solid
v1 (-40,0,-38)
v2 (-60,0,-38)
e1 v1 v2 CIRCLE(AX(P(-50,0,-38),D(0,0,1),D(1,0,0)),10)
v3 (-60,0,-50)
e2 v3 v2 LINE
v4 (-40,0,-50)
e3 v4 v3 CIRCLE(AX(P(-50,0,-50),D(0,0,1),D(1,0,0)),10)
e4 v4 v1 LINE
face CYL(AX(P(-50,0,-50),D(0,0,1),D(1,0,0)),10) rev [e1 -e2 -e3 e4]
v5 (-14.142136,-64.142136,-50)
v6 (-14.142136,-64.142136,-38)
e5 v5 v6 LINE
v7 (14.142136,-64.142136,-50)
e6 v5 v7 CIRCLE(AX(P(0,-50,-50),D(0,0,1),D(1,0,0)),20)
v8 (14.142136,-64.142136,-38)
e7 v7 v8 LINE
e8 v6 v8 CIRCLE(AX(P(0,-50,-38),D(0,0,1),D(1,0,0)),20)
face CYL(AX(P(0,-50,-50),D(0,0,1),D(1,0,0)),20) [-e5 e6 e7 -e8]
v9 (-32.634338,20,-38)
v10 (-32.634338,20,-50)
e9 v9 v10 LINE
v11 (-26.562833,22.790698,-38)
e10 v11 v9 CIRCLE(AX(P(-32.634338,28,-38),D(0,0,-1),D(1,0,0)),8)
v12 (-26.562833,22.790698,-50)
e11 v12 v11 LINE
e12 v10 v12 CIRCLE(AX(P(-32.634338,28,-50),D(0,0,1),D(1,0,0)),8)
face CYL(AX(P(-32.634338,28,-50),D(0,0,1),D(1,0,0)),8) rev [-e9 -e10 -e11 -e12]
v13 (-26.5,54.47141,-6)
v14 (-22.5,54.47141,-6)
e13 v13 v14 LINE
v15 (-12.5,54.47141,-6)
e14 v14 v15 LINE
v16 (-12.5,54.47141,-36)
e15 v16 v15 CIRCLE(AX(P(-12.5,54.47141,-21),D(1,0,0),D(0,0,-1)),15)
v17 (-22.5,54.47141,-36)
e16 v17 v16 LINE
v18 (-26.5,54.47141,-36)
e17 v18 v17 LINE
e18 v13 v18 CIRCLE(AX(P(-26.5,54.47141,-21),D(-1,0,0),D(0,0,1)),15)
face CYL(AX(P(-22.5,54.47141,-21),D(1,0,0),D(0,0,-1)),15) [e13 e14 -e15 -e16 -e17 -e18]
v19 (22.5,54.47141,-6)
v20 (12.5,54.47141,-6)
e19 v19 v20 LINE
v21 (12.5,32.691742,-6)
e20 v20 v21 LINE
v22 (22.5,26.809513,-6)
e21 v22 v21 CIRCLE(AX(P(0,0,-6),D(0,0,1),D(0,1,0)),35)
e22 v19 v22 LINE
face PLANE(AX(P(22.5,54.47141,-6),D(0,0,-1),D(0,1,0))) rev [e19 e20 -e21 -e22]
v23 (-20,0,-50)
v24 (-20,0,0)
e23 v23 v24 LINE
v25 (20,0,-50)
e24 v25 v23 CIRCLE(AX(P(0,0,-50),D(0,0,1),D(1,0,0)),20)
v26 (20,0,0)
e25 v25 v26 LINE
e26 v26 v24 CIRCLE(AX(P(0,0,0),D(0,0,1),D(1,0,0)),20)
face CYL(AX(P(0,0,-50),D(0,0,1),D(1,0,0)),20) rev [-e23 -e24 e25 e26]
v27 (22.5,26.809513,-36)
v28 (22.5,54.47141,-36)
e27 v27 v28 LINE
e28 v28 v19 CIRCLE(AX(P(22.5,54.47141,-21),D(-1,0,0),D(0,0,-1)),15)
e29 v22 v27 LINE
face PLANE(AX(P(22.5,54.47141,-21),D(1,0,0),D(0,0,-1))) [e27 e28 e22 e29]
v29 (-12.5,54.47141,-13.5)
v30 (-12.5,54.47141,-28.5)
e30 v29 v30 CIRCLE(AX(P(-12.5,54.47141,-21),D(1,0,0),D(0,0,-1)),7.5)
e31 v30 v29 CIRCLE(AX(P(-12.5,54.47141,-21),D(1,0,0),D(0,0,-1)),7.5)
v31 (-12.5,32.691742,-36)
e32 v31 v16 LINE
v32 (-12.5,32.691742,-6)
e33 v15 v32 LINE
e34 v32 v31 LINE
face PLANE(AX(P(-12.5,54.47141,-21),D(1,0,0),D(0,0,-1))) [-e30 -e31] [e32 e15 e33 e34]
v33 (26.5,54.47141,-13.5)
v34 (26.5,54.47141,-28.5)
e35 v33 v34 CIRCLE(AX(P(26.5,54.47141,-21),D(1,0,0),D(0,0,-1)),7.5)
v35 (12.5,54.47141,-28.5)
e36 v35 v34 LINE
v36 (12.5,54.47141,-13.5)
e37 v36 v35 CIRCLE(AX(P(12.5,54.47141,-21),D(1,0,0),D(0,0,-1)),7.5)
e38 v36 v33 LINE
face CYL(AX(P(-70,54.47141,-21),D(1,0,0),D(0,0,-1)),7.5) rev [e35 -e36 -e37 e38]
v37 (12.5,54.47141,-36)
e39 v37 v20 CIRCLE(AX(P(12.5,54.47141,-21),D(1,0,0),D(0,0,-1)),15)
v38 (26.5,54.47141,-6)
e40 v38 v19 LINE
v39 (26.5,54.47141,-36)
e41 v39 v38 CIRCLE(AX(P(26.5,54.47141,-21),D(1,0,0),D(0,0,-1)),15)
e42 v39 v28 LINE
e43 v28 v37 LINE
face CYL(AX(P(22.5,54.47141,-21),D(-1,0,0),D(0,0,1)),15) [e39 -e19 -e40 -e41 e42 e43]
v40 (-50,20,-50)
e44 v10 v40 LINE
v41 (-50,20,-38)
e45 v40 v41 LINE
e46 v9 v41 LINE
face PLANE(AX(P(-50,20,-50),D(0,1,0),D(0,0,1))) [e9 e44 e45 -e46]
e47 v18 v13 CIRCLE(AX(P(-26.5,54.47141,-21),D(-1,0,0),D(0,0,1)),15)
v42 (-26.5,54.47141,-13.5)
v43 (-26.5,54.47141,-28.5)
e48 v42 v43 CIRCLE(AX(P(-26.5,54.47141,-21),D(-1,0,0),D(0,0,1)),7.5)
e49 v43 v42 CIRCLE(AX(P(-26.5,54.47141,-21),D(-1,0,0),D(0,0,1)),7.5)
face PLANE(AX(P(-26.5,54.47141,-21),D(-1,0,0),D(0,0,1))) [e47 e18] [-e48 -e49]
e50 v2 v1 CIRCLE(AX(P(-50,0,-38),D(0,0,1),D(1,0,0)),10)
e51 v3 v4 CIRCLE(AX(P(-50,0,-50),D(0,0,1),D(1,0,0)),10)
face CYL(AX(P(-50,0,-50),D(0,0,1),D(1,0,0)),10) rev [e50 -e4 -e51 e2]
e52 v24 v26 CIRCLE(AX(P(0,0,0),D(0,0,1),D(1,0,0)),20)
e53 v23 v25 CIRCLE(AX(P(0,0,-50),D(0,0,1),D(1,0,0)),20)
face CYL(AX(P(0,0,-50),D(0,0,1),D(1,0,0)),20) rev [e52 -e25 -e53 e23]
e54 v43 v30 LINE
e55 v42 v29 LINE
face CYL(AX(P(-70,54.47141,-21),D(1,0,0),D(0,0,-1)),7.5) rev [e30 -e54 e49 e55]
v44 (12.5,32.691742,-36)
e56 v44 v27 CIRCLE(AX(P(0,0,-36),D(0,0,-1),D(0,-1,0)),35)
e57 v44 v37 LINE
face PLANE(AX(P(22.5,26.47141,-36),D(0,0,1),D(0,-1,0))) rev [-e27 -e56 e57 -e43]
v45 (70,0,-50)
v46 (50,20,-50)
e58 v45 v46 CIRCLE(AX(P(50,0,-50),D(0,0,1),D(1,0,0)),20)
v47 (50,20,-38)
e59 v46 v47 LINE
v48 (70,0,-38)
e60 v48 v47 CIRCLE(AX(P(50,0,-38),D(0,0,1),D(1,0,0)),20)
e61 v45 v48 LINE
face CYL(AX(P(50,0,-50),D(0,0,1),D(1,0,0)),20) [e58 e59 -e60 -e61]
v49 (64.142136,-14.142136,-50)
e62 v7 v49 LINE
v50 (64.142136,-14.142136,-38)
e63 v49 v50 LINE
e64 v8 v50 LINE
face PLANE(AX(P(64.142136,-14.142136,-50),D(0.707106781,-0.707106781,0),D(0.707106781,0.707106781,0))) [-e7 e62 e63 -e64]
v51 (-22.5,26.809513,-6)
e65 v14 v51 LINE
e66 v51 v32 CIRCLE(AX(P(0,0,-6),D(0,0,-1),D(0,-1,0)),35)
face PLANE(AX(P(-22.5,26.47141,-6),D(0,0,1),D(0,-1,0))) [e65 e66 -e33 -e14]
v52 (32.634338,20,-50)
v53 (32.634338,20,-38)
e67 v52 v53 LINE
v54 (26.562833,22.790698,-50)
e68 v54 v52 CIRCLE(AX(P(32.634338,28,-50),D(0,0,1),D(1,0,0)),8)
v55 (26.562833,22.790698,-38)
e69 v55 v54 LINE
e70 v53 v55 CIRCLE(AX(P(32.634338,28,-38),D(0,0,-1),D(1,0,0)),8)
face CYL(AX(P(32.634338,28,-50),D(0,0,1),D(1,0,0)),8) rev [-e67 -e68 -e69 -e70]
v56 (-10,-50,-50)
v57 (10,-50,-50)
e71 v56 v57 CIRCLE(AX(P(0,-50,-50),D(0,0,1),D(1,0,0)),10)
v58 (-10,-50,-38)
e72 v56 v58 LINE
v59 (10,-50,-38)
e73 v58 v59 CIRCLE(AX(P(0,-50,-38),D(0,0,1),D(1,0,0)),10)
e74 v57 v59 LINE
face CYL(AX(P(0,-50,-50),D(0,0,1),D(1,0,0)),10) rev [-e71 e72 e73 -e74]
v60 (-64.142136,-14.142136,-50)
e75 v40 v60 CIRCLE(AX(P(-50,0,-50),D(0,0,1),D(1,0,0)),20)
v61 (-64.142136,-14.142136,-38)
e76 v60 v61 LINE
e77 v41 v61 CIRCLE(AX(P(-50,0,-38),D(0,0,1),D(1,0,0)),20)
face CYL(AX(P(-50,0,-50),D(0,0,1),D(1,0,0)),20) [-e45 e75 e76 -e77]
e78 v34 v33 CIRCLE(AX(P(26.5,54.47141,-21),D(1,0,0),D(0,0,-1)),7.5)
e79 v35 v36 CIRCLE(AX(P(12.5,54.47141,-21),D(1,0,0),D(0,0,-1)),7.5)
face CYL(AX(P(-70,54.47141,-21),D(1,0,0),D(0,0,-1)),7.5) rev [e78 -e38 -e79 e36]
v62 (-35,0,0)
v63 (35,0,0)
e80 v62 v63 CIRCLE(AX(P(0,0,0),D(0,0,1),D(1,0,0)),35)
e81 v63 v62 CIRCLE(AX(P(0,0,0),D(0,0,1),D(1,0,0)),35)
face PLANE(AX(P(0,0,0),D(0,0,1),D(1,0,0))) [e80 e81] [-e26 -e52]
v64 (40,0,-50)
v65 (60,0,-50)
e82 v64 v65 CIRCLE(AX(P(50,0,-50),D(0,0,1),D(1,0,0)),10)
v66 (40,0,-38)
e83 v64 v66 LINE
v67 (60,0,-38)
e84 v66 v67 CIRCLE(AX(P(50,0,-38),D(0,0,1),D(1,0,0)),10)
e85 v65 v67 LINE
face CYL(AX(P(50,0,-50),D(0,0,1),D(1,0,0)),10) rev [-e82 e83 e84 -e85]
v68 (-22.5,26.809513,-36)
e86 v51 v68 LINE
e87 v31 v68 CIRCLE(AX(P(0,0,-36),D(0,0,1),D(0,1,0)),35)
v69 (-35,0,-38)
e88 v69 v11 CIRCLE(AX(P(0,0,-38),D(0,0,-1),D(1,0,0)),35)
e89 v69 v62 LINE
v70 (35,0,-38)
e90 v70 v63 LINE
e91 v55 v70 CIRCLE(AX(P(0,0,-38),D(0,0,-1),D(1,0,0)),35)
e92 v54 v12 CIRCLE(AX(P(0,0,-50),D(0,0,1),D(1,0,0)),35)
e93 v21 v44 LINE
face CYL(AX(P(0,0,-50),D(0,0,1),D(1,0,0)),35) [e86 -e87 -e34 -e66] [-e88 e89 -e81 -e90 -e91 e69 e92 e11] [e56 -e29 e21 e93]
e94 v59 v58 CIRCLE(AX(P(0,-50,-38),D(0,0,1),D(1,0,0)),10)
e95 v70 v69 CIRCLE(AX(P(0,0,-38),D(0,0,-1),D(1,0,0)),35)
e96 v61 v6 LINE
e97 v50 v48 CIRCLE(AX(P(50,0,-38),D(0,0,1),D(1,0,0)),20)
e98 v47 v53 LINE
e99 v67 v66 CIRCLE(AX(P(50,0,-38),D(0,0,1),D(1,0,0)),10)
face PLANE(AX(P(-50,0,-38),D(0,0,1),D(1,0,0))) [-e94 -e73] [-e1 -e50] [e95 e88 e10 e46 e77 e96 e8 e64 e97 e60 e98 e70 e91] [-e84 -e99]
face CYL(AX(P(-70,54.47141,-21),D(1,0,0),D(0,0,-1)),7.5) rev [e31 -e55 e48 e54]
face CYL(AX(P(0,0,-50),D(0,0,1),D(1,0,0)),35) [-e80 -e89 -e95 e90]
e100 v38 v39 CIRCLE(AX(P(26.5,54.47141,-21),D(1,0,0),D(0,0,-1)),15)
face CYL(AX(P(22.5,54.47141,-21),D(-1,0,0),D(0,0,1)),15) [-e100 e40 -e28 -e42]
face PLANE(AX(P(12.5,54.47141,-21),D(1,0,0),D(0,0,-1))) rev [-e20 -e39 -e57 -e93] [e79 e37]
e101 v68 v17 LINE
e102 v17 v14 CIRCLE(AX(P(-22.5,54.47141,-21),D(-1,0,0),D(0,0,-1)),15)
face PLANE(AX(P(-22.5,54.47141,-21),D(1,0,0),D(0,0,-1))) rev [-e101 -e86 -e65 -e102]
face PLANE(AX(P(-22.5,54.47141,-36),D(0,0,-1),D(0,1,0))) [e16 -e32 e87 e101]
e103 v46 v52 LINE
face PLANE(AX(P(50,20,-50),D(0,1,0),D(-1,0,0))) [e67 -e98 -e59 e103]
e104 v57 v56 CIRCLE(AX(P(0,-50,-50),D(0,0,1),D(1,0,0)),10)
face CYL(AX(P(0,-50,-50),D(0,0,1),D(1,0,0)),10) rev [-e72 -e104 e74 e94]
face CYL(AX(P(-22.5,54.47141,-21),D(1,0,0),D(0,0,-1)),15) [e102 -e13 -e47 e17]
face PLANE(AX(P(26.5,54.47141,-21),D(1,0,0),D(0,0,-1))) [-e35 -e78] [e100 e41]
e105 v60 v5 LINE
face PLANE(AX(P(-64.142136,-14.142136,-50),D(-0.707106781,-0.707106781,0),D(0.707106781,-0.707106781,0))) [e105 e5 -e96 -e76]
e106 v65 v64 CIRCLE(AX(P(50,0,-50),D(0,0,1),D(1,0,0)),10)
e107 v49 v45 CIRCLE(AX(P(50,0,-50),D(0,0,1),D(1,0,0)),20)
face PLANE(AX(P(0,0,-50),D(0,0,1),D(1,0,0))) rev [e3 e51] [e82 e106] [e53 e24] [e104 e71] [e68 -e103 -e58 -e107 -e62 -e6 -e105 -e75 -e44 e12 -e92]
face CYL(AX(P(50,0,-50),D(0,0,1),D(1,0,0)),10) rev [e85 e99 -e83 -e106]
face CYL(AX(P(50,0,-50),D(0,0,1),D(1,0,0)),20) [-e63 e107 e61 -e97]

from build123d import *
from build123d.topology import SkipClean

# Parameters (mm, degrees)
HUB_SKETCH_R                   = 35
BEARING_HUB_DEPTH              = 50
BORE_SKETCH_R                  = 20
BEARING_BORE_40_DEPTH          = 71.356236397
MOUNTING_FLANGE_DEPTH          = 12
FLANGE_FILLETS_R8_R            = 8
FLANGE_HOLES_SKETCH_R          = 10
FLANGE_MOUNTING_HOLES_20_DEPTH = 12
CLEVIS_LUG_1_DEPTH             = 10
LUG_1_BOSS_SKETCH_R            = 15
LUG_1_BOSS_30_DEPTH            = 4
CLEVIS_START                   = -10
CLEVIS_LUG_2_DEPTH             = 10
LUG_START                      = 4
LUG_2_BOSS_SKETCH_R            = 15
LUG_2_BOSS_30_DEPTH            = 4
PIN_HOLE_SKETCH_R              = 7.5
LUG_PIN_HOLE_15_DEPTH          = 130.275867818


with BuildPart() as part:
    # Hub Sketch → Bearing Hub (new body)
    with BuildSketch(Plane.XY):
        Circle(HUB_SKETCH_R)
    extrude(amount=-BEARING_HUB_DEPTH)

    # Bore Sketch → Bearing Bore Ø40 (cut, through all)
    with BuildSketch(Plane.XY):
        Circle(BORE_SKETCH_R)
    extrude(amount=-BEARING_BORE_40_DEPTH, mode=Mode.SUBTRACT)

    # Flange Profile Sketch → Mounting Flange (add)
    with BuildSketch(Plane.XY.offset(-38)):
        with BuildLine():
            Line((-50, 20), (-28.722813233, 20))
            ThreePointArc((-28.722813233, 20), (0, -35), (28.722813233, 20))
            Line((28.722813233, 20), (50, 20))
            ThreePointArc((50, 20), (68.47759065, 7.653668647), (64.142135624, -14.142135624))
            Line((64.142135624, -14.142135624), (14.142135624, -64.142135624))
            ThreePointArc((14.142135624, -64.142135624), (0, -70), (-14.142135624, -64.142135624))
            Line((-14.142135624, -64.142135624), (-64.142135624, -14.142135624))
            ThreePointArc((-64.142135624, -14.142135624), (-68.47759065, 7.653668647), (-50, 20))
        make_face()
    extrude(amount=-MOUNTING_FLANGE_DEPTH)

    # Flange Fillets R8
    flange_fillets_r8_edges = [part.edges().sort_by_distance(p)[0] for p in [
        (-28.722813233, 20, -44),
        (28.722813233, 20, -44),
    ]]
    fillet(flange_fillets_r8_edges, radius=FLANGE_FILLETS_R8_R)

    # Flange Holes Sketch → Flange Mounting Holes Ø20 (cut)
    with BuildSketch(Plane.XY.offset(-38)):
        with Locations((50, 0)):
            Circle(FLANGE_HOLES_SKETCH_R)
        with Locations((0, -50)):
            Circle(FLANGE_HOLES_SKETCH_R)
        with Locations((-50, 0)):
            Circle(FLANGE_HOLES_SKETCH_R)
    extrude(amount=-FLANGE_MOUNTING_HOLES_20_DEPTH, mode=Mode.SUBTRACT)

    # Lug 1 Profile Sketch → Clevis Lug 1 (add)
    with BuildSketch(Plane(origin=(12.5, 0, 0), x_dir=(0, 0, -1), z_dir=(1, 0, 0))):
        with BuildLine():
            Line((6, 54.471410374), (6, 26.471410374))
            Line((6, 26.471410374), (36, 26.471410374))
            Line((36, 26.471410374), (36, 54.471410374))
            ThreePointArc((36, 54.471410374), (21, 69.471410374), (6, 54.471410374))
        make_face()
    extrude(amount=CLEVIS_LUG_1_DEPTH)

    # Lug 1 Boss Sketch → Lug 1 Boss Ø30 (add)
    with BuildSketch(Plane(origin=(22.5, 0, 0), x_dir=(0, 0, -1), z_dir=(1, 0, 0))):
        with Locations((21, 54.471410374)):
            Circle(LUG_1_BOSS_SKETCH_R)
    extrude(amount=LUG_1_BOSS_30_DEPTH)

    # Lug 2 Profile Sketch → Clevis Lug 2 (add)
    with BuildSketch(Plane(origin=(-12.5, 0, 0), x_dir=(0, 0, -1), z_dir=(1, 0, 0)).offset(CLEVIS_START)):
        with BuildLine():
            Line((36, 54.471410374), (36, 26.471410374))
            Line((36, 26.471410374), (6, 26.471410374))
            Line((6, 26.471410374), (6, 54.471410374))
            ThreePointArc((6, 54.471410374), (21, 69.471410374), (36, 54.471410374))
        make_face()
    extrude(amount=CLEVIS_LUG_2_DEPTH)

    # Lug 2 Boss Sketch → Lug 2 Boss Ø30 (add)
    with SkipClean():  # the faces are left unmerged after this step: merging them gives an invalid solid
        with BuildSketch(Plane.ZY.offset(22.5).offset(LUG_START)):
            with Locations(Location((-21, 54.471410374, 0), (0, 0, 180))):
                Circle(LUG_2_BOSS_SKETCH_R)
        extrude(amount=-LUG_2_BOSS_30_DEPTH)

    # Pin Hole Sketch → Lug Pin Hole Ø15 (cut, through all)
    with SkipClean():  # the faces are left unmerged after this step: merging them gives an invalid solid
        with BuildSketch(Plane(origin=(26.5, 0, 0), x_dir=(0, 0, -1), z_dir=(1, 0, 0))):
            with Locations((21, 54.471410374)):
                Circle(PIN_HOLE_SKETCH_R)
        extrude(amount=-LUG_PIN_HOLE_15_DEPTH, mode=Mode.SUBTRACT)


solid = part.part
